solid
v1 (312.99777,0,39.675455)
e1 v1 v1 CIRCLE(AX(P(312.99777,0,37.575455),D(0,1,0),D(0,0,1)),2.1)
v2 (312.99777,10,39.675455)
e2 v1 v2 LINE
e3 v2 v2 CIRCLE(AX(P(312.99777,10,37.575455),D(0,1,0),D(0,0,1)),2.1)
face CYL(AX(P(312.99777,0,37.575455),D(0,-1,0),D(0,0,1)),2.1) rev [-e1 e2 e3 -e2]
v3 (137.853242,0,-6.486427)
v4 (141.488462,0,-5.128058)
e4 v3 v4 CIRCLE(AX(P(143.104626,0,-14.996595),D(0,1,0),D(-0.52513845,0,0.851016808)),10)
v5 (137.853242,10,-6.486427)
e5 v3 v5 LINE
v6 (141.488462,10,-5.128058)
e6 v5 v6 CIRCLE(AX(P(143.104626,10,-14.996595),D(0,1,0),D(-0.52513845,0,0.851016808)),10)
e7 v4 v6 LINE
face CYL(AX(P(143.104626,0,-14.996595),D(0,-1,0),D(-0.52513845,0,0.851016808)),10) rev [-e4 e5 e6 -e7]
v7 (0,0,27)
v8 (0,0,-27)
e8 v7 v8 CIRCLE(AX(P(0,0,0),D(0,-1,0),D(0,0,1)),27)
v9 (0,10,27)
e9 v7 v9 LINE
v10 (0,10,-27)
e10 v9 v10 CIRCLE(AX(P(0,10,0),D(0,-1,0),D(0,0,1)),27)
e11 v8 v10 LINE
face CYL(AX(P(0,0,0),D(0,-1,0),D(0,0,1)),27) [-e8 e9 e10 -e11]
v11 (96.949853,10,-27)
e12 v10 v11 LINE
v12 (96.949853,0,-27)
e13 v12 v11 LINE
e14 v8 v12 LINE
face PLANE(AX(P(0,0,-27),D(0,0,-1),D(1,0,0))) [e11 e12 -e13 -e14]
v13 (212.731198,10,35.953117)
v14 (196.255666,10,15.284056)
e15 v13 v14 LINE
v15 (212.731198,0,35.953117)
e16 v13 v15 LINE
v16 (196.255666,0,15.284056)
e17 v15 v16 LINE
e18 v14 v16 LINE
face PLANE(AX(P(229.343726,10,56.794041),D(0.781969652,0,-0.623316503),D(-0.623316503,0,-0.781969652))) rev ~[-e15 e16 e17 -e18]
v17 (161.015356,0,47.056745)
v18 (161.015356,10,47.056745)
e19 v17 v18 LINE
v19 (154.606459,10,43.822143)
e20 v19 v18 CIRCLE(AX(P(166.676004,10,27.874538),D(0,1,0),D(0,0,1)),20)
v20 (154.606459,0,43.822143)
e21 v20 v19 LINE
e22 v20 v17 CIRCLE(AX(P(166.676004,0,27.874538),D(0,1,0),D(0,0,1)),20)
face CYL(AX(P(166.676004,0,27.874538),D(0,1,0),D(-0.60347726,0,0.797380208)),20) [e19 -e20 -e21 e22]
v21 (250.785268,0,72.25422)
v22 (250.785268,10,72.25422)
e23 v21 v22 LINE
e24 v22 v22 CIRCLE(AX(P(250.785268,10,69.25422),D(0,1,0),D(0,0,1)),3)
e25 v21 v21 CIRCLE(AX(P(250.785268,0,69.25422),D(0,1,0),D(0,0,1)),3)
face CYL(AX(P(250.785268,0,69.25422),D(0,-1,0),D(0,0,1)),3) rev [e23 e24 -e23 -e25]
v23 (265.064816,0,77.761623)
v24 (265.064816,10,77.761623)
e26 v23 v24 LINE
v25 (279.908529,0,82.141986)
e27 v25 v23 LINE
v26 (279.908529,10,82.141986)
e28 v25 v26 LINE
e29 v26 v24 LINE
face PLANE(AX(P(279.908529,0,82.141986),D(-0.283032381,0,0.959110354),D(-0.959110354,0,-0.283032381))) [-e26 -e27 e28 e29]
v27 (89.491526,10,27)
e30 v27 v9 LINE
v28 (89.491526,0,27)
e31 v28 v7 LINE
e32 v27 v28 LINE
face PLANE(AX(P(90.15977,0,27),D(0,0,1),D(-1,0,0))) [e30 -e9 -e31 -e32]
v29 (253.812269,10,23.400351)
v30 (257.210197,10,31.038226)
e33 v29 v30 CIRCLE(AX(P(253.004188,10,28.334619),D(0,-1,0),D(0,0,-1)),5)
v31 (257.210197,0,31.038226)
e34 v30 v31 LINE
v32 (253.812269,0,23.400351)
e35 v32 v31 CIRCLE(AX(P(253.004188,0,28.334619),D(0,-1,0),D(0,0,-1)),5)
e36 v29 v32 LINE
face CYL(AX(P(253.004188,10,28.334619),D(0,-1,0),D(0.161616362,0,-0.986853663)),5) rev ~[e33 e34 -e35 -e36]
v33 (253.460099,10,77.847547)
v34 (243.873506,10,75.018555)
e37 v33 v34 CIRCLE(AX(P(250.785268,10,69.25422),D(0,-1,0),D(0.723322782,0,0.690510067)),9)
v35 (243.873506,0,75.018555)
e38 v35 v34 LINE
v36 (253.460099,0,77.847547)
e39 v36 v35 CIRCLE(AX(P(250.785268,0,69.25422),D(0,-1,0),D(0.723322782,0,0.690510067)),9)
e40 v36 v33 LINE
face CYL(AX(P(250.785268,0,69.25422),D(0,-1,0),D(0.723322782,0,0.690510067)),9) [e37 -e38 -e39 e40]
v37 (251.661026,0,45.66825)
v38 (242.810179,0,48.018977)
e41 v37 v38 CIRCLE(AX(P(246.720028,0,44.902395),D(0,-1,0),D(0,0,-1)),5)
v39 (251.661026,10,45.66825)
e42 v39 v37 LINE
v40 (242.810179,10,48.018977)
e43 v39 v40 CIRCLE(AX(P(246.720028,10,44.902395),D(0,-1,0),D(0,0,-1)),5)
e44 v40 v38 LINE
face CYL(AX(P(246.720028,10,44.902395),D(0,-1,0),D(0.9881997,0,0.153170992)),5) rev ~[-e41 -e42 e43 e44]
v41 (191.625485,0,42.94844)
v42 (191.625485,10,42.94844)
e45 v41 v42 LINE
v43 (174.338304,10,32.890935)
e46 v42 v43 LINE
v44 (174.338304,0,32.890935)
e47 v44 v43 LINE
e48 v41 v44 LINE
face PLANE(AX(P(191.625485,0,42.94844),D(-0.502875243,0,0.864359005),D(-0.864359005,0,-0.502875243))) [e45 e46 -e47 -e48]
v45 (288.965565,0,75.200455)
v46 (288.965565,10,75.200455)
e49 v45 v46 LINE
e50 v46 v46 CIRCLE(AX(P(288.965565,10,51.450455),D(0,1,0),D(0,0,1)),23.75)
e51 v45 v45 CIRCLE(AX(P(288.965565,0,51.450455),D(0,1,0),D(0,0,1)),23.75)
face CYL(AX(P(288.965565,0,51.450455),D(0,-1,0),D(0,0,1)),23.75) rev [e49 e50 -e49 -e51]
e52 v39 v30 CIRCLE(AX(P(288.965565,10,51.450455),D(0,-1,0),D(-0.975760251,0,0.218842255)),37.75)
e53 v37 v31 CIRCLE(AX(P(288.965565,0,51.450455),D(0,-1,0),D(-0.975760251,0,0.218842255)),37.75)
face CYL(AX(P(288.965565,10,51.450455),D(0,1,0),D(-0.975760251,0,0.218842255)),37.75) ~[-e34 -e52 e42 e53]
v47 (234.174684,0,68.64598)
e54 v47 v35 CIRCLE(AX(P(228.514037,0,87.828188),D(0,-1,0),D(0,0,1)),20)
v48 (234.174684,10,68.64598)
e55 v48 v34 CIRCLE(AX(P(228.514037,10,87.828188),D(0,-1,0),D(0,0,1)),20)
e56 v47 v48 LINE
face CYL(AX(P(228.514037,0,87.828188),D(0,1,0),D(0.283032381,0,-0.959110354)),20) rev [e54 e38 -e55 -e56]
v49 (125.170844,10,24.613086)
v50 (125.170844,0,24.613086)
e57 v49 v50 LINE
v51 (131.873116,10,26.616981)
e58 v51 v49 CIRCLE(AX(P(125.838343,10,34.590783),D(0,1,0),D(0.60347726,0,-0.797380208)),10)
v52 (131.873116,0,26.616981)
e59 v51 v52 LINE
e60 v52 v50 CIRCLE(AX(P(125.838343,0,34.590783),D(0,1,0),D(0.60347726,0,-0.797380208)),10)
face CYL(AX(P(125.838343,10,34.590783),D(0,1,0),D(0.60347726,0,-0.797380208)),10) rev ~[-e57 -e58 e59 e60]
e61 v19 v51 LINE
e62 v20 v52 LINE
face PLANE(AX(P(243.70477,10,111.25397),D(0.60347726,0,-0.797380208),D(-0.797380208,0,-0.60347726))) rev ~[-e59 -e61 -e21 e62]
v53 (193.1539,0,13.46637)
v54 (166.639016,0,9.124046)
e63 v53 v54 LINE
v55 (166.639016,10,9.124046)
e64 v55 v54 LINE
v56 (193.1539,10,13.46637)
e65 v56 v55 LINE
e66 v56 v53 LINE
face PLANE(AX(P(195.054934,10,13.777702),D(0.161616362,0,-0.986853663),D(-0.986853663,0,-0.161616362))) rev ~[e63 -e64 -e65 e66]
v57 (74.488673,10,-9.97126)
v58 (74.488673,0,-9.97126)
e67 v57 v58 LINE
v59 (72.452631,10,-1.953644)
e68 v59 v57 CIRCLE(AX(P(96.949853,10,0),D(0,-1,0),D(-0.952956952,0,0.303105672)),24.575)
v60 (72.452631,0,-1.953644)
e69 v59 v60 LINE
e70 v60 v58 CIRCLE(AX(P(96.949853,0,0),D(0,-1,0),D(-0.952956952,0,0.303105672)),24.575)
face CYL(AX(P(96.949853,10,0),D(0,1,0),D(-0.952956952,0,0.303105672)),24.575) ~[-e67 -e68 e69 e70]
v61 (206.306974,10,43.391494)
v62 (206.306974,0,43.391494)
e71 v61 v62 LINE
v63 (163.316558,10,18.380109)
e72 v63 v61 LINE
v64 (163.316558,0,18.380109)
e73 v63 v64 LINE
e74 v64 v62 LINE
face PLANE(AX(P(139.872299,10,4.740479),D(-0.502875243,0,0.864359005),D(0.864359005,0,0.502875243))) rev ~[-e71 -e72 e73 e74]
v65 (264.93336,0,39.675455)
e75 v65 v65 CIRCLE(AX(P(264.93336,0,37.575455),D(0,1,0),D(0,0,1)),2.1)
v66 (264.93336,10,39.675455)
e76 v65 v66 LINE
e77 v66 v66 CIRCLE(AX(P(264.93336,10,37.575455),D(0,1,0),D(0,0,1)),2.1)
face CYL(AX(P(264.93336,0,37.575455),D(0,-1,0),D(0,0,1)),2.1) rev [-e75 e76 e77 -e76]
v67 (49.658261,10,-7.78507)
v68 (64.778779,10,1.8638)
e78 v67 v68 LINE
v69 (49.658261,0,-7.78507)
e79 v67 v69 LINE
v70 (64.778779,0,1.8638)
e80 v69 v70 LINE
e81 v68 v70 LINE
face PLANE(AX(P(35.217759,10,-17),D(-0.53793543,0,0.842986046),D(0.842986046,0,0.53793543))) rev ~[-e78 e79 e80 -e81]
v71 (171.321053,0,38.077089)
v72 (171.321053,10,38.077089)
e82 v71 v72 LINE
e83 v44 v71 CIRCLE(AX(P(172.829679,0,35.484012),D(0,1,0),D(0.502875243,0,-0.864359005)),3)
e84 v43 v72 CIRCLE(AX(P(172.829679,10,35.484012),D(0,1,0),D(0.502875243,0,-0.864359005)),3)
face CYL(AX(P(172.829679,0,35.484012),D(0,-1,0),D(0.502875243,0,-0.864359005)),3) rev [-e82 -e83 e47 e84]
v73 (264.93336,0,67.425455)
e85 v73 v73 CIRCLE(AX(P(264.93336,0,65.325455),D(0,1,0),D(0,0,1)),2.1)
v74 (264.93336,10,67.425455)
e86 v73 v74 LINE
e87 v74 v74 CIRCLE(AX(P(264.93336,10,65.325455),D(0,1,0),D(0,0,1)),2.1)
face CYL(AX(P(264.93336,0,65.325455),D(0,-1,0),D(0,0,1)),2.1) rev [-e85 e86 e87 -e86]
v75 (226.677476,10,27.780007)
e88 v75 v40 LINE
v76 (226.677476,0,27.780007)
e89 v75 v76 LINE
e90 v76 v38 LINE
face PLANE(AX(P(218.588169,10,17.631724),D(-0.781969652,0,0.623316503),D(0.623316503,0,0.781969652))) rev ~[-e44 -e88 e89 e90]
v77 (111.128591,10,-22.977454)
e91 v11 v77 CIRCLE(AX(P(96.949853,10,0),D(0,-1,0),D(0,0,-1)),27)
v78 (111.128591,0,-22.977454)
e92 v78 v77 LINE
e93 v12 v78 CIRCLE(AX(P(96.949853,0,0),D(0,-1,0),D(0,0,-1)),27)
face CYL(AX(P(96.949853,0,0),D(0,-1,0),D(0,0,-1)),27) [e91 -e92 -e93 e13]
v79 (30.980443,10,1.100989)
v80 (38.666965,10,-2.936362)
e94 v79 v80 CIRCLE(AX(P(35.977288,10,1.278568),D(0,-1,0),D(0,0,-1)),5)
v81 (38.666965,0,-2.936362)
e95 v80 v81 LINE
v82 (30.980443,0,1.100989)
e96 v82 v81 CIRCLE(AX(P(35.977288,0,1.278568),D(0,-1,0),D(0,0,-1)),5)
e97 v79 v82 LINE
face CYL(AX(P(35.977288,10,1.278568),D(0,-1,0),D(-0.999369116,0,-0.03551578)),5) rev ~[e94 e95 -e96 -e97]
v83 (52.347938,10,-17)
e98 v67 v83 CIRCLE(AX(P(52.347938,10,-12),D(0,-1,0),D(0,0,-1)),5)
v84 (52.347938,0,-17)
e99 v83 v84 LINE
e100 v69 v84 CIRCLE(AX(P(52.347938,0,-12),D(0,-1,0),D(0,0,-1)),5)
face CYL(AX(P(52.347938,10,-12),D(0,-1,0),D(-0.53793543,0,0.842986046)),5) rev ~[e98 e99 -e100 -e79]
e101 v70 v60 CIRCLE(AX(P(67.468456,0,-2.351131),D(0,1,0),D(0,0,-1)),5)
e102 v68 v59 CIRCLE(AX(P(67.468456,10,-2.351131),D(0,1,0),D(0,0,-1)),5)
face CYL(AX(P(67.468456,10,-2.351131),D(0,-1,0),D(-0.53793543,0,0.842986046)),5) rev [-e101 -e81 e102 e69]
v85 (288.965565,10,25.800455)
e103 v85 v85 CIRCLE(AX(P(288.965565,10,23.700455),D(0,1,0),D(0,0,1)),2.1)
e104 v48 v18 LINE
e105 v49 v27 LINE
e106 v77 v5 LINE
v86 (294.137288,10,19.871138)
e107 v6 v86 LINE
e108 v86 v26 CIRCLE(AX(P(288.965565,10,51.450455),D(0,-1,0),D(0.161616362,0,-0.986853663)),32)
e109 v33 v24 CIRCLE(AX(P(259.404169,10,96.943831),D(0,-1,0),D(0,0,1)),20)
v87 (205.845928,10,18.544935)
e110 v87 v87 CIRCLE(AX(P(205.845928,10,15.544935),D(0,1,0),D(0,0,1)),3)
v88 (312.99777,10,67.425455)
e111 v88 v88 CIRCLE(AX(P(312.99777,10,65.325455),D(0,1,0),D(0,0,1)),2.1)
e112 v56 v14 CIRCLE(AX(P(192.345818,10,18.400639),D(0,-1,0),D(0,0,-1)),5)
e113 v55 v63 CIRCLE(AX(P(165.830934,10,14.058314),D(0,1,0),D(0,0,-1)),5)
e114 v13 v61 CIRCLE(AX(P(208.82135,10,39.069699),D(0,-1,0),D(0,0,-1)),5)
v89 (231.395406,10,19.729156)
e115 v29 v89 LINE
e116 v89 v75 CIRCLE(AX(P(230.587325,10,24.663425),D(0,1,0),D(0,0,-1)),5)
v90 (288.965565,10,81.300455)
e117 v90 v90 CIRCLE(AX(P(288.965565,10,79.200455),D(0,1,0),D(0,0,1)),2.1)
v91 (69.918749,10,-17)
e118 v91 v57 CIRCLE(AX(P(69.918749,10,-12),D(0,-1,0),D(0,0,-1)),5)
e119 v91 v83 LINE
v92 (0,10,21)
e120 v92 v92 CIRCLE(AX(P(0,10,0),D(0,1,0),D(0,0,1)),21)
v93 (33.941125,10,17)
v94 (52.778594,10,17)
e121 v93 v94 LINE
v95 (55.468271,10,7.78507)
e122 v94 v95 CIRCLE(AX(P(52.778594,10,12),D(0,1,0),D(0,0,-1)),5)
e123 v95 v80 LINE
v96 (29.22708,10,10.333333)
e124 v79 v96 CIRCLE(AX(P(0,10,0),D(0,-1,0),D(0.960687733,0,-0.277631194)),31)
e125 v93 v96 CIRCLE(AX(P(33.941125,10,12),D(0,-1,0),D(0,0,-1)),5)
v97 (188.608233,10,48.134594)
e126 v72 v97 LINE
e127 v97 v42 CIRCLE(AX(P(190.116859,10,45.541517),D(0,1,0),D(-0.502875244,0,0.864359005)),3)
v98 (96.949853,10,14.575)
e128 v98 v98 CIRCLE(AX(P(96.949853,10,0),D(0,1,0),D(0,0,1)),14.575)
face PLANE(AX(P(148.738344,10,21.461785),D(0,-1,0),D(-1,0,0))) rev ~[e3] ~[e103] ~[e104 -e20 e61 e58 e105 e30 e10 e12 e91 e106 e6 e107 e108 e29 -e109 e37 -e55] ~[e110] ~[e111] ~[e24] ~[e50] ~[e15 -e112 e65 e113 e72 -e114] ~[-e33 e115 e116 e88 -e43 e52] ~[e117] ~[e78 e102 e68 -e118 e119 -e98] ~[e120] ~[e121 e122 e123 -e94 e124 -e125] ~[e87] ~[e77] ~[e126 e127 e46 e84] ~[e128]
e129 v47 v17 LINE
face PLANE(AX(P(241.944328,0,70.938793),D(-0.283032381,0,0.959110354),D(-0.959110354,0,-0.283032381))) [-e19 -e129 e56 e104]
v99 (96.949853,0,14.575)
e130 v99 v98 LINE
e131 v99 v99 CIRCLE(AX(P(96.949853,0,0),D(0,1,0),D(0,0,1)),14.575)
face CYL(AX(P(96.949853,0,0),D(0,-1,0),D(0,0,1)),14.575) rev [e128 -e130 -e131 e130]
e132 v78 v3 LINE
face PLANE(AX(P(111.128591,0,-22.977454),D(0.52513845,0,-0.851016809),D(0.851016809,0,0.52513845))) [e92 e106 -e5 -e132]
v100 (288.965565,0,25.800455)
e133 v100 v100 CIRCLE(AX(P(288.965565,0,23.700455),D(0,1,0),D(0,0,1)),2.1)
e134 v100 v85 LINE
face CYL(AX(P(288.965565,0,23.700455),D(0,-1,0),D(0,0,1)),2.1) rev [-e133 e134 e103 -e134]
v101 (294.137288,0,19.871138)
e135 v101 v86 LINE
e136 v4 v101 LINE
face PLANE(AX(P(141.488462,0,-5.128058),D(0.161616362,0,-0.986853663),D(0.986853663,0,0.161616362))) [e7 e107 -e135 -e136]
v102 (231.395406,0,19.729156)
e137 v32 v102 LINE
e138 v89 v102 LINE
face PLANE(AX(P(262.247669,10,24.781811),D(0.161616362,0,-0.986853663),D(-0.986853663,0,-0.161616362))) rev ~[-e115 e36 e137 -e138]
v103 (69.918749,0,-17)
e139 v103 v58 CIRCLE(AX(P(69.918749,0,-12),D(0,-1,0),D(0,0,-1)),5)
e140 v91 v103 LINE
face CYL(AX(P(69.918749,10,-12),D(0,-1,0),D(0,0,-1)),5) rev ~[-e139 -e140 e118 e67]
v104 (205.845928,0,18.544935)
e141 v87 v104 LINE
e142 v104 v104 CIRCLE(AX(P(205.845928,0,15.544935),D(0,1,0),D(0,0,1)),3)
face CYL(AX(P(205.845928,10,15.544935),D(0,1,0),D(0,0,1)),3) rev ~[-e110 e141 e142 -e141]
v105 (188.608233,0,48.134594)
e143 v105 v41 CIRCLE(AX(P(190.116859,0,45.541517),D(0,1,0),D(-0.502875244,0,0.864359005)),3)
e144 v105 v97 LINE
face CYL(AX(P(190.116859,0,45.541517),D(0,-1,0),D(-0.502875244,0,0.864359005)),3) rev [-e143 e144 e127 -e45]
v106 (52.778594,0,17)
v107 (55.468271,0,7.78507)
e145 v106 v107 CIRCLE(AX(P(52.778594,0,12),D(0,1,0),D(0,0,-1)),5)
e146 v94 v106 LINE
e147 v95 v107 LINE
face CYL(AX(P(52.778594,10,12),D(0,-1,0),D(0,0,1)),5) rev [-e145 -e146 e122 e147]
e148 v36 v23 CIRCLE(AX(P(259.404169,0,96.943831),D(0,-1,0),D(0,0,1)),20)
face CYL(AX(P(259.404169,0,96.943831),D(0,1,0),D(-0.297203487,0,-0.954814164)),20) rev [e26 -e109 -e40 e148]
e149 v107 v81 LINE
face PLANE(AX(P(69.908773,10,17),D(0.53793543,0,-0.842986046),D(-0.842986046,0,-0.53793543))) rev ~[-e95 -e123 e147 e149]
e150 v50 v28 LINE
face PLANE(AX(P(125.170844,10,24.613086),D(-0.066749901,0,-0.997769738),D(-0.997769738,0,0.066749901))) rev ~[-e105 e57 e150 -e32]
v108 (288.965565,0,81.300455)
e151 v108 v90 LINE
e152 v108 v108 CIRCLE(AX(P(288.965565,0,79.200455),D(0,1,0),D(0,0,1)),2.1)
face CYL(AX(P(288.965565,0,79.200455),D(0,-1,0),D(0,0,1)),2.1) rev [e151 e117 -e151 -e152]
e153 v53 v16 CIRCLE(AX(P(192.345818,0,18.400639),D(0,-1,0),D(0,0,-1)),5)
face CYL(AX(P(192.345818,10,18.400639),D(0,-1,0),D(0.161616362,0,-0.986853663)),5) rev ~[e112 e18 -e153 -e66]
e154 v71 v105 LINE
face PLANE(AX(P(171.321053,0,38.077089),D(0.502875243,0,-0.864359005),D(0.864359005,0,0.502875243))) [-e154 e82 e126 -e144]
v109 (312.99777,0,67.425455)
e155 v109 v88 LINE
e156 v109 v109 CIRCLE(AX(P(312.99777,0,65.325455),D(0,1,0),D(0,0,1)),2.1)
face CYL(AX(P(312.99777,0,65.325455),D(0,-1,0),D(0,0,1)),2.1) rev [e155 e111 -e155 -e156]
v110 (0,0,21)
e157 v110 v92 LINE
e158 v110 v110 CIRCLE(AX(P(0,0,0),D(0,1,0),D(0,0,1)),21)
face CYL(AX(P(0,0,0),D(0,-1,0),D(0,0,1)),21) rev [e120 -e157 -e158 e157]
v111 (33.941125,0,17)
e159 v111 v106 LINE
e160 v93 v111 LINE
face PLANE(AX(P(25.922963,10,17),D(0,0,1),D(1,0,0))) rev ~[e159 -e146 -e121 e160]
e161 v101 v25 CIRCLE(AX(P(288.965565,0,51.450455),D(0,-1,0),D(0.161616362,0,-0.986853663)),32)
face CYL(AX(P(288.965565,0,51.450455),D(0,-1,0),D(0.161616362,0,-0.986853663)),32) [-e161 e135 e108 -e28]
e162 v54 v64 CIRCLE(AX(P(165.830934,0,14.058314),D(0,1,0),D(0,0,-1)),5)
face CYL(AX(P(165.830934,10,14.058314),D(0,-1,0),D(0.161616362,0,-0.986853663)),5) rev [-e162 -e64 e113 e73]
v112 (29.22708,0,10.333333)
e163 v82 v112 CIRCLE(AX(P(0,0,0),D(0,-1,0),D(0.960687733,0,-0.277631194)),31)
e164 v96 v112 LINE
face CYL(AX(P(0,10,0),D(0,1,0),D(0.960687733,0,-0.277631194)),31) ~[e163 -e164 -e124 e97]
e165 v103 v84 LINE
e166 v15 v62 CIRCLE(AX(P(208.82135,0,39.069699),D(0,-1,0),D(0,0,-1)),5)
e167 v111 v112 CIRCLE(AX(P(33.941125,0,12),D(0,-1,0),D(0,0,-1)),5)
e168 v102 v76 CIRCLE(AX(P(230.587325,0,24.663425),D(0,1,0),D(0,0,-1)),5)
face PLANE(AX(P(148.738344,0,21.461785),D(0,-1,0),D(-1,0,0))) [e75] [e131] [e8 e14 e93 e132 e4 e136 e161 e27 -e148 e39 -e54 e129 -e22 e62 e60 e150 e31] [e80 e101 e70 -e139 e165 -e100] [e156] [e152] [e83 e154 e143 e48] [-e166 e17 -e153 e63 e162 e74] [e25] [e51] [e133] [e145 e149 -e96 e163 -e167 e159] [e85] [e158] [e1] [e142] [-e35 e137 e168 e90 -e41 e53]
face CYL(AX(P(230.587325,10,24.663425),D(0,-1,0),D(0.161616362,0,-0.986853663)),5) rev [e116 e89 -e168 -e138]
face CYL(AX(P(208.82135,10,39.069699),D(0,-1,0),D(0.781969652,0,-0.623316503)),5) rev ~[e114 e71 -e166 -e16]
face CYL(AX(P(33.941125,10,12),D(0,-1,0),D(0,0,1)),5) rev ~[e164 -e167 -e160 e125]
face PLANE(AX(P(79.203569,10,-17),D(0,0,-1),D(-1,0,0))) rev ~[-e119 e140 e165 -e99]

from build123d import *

# Parameters (mm, degrees)
SKETCH_1_R          = 21
SKETCH_1_R_2        = 14.575
SKETCH_1_R_3        = 23.75
SKETCH_1_R_4        = 2.1
SKETCH_1_R_5        = 3
EXTRUDE_1_DEPTH     = 10
CUT_EXTRUDE_1_DEPTH = 10
FILLET_1_R          = 20
CUT_EXTRUDE_2_DEPTH = 10
FILLET_2_R          = 5
SKETCH_5_R          = 3
CUT_EXTRUDE_3_DEPTH = 10
CUT_EXTRUDE_5_DEPTH = 10


with BuildPart() as part:
    # 草图1 → 凸台-拉伸1 (new body)
    with BuildSketch(Plane(origin=(0, 0, 0), x_dir=(1, 0, 0), z_dir=(0, 1, 0))):
        with BuildLine():
            Line((0, 27), (96.94985335, 27))
            ThreePointArc((96.94985335, 27), (104.319003455, 25.974903787), (111.128591496, 22.977453832))
            Line((111.128591496, 22.977453832), (137.853241587, 6.486426651))
            ThreePointArc((137.853241587, 6.486426651), (139.604326734, 5.629209592), (141.488462469, 5.12805811))
            Line((141.488462469, 5.12805811), (294.137288277, -19.871137584))
            ThreePointArc((294.137288277, -19.871137584), (320.161534926, -58.578669293), (279.908528522, -82.141986125))
            Line((279.908528522, -82.141986125), (257.295172569, -75.46881036))
            ThreePointArc((257.295172569, -75.46881036), (248.237976105, -77.886212941), (241.944328029, -70.938793499))
            Line((241.944328029, -70.938793499), (95.820417973, -27.817792917))
            ThreePointArc((95.820417973, -27.817792917), (93.01947824, -27.205504027), (90.159770359, -27))
            Line((90.159770359, -27), (0, -27))
            ThreePointArc((0, -27), (-27, 0), (0, 27))
        make_face()
        with Locations(Location((0, 0, 0), (0, 0, 270))):
            Circle(SKETCH_1_R, mode=Mode.SUBTRACT)
        with Locations(Location((96.94985335, 0, 0), (0, 0, 270))):
            Circle(SKETCH_1_R_2, mode=Mode.SUBTRACT)
        with Locations(Location((288.965564705, -51.450454792, 0), (0, 0, 270))):
            Circle(SKETCH_1_R_3, mode=Mode.SUBTRACT)
        with Locations(Location((288.965564705, -23.700454792, 0), (0, 0, 270))):
            Circle(SKETCH_1_R_4, mode=Mode.SUBTRACT)
        with Locations(Location((312.99776966, -37.575454792, 0), (0, 0, 270))):
            Circle(SKETCH_1_R_4, mode=Mode.SUBTRACT)
        with Locations(Location((312.99776966, -65.325454792, 0), (0, 0, 270))):
            Circle(SKETCH_1_R_4, mode=Mode.SUBTRACT)
        with Locations(Location((288.965564705, -79.200454792, 0), (0, 0, 270))):
            Circle(SKETCH_1_R_4, mode=Mode.SUBTRACT)
        with Locations(Location((264.93335975, -65.325454792, 0), (0, 0, 270))):
            Circle(SKETCH_1_R_4, mode=Mode.SUBTRACT)
        with Locations(Location((264.93335975, -37.575454792, 0), (0, 0, 270))):
            Circle(SKETCH_1_R_4, mode=Mode.SUBTRACT)
        with Locations(Location((250.785267532, -69.254219754, 0), (0, 0, 270))):
            Circle(SKETCH_1_R_5, mode=Mode.SUBTRACT)
    extrude(amount=EXTRUDE_1_DEPTH)

    # 草图3 → 切除-拉伸1 (cut)
    with BuildSketch(Plane(origin=(0, 10, 0), x_dir=(1, 0, 0), z_dir=(0, 1, 0))):
        with BuildLine():
            Line((243.704770173, -111.253970394), (131.873115991, -26.616980894))
            ThreePointArc((131.873115991, -26.616980894), (128.702921113, -25.009854291), (125.170844375, -24.613085592))
            Line((125.170844375, -24.613085592), (88.824772335, -27.044605234))
            Line((88.824772335, -27.044605234), (243.704770173, -111.253970394))
        make_face()
    extrude(amount=-CUT_EXTRUDE_1_DEPTH, mode=Mode.SUBTRACT)

    # 圆角1
    fillet_1_edges = [part.edges().sort_by_distance(p)[0] for p in [
        (257.295172569, 5, 75.46881036),
        (241.944328029, 5, 70.938793499),
        (157.515855554, 5, 46.024046766),
    ]]
    fillet(fillet_1_edges, radius=FILLET_1_R)

    # 草图4 → 切除-拉伸2 (cut)
    with BuildSketch(Plane(origin=(0, 10, 0), x_dir=(1, 0, 0), z_dir=(0, 1, 0))):
        with BuildLine():
            ThreePointArc((73.530936261, -7.448821877), (73.010770558, 5.554362258), (79.203568528, 17))
            Line((79.203568528, 17), (35.21775864, 17))
            Line((35.21775864, 17), (73.530936261, -7.448821877))
        make_face()
        with BuildLine():
            Line((69.908772681, -17), (29.781319723, 8.606567001))
            ThreePointArc((29.781319723, 8.606567001), (30.653969418, -4.618891526), (25.922962794, -17))
            Line((25.922962794, -17), (69.908772681, -17))
        make_face()
        with BuildLine():
            Line((218.588169342, -17.631723767), (252.130615229, -59.711749917))
            ThreePointArc((252.130615229, -59.711749917), (252.70586007, -40.94824932), (262.247669453, -24.781810782))
            Line((262.247669453, -24.781810782), (218.588169342, -17.631723767))
        make_face()
        Polygon((139.872298853, -4.740478518), (229.34372575, -56.794041123), (195.054934366, -13.777701679), align=None)
    extrude(amount=-CUT_EXTRUDE_2_DEPTH, mode=Mode.SUBTRACT)

    # 圆角2
    fillet_2_edges = [part.edges().sort_by_distance(p)[0] for p in [
        (25.922962794, 5, 17),
        (29.781319723, 5, -8.606567001),
        (69.908772681, 5, 17),
        (139.872298853, 5, 4.740478518),
        (195.054934366, 5, 13.777701679),
        (229.34372575, 5, 56.794041123),
        (262.247669453, 5, 24.781810782),
        (252.130615229, 5, 59.711749917),
        (218.588169342, 5, 17.631723767),
        (79.203568528, 5, -17),
        (73.530936261, 5, 7.448821877),
        (35.21775864, 5, -17),
    ]]
    fillet(fillet_2_edges, radius=FILLET_2_R)

    # 草图5 → 切除-拉伸3 (cut)
    with BuildSketch(Plane(origin=(0, 10, 0), x_dir=(1, 0, 0), z_dir=(0, 1, 0))):
        with Locations(Location((205.845927584, -15.544935392, 0), (0, 0, 270))):
            Circle(SKETCH_5_R)
    extrude(amount=-CUT_EXTRUDE_3_DEPTH, mode=Mode.SUBTRACT)

    # 草图7 → 切除-拉伸5 (cut)
    with BuildSketch(Plane.XZ):
        with BuildLine():
            Line((171.32105295, 38.077089469), (188.608233051, 48.134594337))
            ThreePointArc((188.608233051, 48.134594337), (192.709935796, 47.050143053), (191.625484511, 42.948440307))
            Line((191.625484511, 42.948440307), (174.338304411, 32.890935439))
            ThreePointArc((174.338304411, 32.890935439), (170.236601666, 33.975386724), (171.32105295, 38.077089469))
        make_face()
    extrude(amount=-CUT_EXTRUDE_5_DEPTH, mode=Mode.SUBTRACT)


solid = part.part
